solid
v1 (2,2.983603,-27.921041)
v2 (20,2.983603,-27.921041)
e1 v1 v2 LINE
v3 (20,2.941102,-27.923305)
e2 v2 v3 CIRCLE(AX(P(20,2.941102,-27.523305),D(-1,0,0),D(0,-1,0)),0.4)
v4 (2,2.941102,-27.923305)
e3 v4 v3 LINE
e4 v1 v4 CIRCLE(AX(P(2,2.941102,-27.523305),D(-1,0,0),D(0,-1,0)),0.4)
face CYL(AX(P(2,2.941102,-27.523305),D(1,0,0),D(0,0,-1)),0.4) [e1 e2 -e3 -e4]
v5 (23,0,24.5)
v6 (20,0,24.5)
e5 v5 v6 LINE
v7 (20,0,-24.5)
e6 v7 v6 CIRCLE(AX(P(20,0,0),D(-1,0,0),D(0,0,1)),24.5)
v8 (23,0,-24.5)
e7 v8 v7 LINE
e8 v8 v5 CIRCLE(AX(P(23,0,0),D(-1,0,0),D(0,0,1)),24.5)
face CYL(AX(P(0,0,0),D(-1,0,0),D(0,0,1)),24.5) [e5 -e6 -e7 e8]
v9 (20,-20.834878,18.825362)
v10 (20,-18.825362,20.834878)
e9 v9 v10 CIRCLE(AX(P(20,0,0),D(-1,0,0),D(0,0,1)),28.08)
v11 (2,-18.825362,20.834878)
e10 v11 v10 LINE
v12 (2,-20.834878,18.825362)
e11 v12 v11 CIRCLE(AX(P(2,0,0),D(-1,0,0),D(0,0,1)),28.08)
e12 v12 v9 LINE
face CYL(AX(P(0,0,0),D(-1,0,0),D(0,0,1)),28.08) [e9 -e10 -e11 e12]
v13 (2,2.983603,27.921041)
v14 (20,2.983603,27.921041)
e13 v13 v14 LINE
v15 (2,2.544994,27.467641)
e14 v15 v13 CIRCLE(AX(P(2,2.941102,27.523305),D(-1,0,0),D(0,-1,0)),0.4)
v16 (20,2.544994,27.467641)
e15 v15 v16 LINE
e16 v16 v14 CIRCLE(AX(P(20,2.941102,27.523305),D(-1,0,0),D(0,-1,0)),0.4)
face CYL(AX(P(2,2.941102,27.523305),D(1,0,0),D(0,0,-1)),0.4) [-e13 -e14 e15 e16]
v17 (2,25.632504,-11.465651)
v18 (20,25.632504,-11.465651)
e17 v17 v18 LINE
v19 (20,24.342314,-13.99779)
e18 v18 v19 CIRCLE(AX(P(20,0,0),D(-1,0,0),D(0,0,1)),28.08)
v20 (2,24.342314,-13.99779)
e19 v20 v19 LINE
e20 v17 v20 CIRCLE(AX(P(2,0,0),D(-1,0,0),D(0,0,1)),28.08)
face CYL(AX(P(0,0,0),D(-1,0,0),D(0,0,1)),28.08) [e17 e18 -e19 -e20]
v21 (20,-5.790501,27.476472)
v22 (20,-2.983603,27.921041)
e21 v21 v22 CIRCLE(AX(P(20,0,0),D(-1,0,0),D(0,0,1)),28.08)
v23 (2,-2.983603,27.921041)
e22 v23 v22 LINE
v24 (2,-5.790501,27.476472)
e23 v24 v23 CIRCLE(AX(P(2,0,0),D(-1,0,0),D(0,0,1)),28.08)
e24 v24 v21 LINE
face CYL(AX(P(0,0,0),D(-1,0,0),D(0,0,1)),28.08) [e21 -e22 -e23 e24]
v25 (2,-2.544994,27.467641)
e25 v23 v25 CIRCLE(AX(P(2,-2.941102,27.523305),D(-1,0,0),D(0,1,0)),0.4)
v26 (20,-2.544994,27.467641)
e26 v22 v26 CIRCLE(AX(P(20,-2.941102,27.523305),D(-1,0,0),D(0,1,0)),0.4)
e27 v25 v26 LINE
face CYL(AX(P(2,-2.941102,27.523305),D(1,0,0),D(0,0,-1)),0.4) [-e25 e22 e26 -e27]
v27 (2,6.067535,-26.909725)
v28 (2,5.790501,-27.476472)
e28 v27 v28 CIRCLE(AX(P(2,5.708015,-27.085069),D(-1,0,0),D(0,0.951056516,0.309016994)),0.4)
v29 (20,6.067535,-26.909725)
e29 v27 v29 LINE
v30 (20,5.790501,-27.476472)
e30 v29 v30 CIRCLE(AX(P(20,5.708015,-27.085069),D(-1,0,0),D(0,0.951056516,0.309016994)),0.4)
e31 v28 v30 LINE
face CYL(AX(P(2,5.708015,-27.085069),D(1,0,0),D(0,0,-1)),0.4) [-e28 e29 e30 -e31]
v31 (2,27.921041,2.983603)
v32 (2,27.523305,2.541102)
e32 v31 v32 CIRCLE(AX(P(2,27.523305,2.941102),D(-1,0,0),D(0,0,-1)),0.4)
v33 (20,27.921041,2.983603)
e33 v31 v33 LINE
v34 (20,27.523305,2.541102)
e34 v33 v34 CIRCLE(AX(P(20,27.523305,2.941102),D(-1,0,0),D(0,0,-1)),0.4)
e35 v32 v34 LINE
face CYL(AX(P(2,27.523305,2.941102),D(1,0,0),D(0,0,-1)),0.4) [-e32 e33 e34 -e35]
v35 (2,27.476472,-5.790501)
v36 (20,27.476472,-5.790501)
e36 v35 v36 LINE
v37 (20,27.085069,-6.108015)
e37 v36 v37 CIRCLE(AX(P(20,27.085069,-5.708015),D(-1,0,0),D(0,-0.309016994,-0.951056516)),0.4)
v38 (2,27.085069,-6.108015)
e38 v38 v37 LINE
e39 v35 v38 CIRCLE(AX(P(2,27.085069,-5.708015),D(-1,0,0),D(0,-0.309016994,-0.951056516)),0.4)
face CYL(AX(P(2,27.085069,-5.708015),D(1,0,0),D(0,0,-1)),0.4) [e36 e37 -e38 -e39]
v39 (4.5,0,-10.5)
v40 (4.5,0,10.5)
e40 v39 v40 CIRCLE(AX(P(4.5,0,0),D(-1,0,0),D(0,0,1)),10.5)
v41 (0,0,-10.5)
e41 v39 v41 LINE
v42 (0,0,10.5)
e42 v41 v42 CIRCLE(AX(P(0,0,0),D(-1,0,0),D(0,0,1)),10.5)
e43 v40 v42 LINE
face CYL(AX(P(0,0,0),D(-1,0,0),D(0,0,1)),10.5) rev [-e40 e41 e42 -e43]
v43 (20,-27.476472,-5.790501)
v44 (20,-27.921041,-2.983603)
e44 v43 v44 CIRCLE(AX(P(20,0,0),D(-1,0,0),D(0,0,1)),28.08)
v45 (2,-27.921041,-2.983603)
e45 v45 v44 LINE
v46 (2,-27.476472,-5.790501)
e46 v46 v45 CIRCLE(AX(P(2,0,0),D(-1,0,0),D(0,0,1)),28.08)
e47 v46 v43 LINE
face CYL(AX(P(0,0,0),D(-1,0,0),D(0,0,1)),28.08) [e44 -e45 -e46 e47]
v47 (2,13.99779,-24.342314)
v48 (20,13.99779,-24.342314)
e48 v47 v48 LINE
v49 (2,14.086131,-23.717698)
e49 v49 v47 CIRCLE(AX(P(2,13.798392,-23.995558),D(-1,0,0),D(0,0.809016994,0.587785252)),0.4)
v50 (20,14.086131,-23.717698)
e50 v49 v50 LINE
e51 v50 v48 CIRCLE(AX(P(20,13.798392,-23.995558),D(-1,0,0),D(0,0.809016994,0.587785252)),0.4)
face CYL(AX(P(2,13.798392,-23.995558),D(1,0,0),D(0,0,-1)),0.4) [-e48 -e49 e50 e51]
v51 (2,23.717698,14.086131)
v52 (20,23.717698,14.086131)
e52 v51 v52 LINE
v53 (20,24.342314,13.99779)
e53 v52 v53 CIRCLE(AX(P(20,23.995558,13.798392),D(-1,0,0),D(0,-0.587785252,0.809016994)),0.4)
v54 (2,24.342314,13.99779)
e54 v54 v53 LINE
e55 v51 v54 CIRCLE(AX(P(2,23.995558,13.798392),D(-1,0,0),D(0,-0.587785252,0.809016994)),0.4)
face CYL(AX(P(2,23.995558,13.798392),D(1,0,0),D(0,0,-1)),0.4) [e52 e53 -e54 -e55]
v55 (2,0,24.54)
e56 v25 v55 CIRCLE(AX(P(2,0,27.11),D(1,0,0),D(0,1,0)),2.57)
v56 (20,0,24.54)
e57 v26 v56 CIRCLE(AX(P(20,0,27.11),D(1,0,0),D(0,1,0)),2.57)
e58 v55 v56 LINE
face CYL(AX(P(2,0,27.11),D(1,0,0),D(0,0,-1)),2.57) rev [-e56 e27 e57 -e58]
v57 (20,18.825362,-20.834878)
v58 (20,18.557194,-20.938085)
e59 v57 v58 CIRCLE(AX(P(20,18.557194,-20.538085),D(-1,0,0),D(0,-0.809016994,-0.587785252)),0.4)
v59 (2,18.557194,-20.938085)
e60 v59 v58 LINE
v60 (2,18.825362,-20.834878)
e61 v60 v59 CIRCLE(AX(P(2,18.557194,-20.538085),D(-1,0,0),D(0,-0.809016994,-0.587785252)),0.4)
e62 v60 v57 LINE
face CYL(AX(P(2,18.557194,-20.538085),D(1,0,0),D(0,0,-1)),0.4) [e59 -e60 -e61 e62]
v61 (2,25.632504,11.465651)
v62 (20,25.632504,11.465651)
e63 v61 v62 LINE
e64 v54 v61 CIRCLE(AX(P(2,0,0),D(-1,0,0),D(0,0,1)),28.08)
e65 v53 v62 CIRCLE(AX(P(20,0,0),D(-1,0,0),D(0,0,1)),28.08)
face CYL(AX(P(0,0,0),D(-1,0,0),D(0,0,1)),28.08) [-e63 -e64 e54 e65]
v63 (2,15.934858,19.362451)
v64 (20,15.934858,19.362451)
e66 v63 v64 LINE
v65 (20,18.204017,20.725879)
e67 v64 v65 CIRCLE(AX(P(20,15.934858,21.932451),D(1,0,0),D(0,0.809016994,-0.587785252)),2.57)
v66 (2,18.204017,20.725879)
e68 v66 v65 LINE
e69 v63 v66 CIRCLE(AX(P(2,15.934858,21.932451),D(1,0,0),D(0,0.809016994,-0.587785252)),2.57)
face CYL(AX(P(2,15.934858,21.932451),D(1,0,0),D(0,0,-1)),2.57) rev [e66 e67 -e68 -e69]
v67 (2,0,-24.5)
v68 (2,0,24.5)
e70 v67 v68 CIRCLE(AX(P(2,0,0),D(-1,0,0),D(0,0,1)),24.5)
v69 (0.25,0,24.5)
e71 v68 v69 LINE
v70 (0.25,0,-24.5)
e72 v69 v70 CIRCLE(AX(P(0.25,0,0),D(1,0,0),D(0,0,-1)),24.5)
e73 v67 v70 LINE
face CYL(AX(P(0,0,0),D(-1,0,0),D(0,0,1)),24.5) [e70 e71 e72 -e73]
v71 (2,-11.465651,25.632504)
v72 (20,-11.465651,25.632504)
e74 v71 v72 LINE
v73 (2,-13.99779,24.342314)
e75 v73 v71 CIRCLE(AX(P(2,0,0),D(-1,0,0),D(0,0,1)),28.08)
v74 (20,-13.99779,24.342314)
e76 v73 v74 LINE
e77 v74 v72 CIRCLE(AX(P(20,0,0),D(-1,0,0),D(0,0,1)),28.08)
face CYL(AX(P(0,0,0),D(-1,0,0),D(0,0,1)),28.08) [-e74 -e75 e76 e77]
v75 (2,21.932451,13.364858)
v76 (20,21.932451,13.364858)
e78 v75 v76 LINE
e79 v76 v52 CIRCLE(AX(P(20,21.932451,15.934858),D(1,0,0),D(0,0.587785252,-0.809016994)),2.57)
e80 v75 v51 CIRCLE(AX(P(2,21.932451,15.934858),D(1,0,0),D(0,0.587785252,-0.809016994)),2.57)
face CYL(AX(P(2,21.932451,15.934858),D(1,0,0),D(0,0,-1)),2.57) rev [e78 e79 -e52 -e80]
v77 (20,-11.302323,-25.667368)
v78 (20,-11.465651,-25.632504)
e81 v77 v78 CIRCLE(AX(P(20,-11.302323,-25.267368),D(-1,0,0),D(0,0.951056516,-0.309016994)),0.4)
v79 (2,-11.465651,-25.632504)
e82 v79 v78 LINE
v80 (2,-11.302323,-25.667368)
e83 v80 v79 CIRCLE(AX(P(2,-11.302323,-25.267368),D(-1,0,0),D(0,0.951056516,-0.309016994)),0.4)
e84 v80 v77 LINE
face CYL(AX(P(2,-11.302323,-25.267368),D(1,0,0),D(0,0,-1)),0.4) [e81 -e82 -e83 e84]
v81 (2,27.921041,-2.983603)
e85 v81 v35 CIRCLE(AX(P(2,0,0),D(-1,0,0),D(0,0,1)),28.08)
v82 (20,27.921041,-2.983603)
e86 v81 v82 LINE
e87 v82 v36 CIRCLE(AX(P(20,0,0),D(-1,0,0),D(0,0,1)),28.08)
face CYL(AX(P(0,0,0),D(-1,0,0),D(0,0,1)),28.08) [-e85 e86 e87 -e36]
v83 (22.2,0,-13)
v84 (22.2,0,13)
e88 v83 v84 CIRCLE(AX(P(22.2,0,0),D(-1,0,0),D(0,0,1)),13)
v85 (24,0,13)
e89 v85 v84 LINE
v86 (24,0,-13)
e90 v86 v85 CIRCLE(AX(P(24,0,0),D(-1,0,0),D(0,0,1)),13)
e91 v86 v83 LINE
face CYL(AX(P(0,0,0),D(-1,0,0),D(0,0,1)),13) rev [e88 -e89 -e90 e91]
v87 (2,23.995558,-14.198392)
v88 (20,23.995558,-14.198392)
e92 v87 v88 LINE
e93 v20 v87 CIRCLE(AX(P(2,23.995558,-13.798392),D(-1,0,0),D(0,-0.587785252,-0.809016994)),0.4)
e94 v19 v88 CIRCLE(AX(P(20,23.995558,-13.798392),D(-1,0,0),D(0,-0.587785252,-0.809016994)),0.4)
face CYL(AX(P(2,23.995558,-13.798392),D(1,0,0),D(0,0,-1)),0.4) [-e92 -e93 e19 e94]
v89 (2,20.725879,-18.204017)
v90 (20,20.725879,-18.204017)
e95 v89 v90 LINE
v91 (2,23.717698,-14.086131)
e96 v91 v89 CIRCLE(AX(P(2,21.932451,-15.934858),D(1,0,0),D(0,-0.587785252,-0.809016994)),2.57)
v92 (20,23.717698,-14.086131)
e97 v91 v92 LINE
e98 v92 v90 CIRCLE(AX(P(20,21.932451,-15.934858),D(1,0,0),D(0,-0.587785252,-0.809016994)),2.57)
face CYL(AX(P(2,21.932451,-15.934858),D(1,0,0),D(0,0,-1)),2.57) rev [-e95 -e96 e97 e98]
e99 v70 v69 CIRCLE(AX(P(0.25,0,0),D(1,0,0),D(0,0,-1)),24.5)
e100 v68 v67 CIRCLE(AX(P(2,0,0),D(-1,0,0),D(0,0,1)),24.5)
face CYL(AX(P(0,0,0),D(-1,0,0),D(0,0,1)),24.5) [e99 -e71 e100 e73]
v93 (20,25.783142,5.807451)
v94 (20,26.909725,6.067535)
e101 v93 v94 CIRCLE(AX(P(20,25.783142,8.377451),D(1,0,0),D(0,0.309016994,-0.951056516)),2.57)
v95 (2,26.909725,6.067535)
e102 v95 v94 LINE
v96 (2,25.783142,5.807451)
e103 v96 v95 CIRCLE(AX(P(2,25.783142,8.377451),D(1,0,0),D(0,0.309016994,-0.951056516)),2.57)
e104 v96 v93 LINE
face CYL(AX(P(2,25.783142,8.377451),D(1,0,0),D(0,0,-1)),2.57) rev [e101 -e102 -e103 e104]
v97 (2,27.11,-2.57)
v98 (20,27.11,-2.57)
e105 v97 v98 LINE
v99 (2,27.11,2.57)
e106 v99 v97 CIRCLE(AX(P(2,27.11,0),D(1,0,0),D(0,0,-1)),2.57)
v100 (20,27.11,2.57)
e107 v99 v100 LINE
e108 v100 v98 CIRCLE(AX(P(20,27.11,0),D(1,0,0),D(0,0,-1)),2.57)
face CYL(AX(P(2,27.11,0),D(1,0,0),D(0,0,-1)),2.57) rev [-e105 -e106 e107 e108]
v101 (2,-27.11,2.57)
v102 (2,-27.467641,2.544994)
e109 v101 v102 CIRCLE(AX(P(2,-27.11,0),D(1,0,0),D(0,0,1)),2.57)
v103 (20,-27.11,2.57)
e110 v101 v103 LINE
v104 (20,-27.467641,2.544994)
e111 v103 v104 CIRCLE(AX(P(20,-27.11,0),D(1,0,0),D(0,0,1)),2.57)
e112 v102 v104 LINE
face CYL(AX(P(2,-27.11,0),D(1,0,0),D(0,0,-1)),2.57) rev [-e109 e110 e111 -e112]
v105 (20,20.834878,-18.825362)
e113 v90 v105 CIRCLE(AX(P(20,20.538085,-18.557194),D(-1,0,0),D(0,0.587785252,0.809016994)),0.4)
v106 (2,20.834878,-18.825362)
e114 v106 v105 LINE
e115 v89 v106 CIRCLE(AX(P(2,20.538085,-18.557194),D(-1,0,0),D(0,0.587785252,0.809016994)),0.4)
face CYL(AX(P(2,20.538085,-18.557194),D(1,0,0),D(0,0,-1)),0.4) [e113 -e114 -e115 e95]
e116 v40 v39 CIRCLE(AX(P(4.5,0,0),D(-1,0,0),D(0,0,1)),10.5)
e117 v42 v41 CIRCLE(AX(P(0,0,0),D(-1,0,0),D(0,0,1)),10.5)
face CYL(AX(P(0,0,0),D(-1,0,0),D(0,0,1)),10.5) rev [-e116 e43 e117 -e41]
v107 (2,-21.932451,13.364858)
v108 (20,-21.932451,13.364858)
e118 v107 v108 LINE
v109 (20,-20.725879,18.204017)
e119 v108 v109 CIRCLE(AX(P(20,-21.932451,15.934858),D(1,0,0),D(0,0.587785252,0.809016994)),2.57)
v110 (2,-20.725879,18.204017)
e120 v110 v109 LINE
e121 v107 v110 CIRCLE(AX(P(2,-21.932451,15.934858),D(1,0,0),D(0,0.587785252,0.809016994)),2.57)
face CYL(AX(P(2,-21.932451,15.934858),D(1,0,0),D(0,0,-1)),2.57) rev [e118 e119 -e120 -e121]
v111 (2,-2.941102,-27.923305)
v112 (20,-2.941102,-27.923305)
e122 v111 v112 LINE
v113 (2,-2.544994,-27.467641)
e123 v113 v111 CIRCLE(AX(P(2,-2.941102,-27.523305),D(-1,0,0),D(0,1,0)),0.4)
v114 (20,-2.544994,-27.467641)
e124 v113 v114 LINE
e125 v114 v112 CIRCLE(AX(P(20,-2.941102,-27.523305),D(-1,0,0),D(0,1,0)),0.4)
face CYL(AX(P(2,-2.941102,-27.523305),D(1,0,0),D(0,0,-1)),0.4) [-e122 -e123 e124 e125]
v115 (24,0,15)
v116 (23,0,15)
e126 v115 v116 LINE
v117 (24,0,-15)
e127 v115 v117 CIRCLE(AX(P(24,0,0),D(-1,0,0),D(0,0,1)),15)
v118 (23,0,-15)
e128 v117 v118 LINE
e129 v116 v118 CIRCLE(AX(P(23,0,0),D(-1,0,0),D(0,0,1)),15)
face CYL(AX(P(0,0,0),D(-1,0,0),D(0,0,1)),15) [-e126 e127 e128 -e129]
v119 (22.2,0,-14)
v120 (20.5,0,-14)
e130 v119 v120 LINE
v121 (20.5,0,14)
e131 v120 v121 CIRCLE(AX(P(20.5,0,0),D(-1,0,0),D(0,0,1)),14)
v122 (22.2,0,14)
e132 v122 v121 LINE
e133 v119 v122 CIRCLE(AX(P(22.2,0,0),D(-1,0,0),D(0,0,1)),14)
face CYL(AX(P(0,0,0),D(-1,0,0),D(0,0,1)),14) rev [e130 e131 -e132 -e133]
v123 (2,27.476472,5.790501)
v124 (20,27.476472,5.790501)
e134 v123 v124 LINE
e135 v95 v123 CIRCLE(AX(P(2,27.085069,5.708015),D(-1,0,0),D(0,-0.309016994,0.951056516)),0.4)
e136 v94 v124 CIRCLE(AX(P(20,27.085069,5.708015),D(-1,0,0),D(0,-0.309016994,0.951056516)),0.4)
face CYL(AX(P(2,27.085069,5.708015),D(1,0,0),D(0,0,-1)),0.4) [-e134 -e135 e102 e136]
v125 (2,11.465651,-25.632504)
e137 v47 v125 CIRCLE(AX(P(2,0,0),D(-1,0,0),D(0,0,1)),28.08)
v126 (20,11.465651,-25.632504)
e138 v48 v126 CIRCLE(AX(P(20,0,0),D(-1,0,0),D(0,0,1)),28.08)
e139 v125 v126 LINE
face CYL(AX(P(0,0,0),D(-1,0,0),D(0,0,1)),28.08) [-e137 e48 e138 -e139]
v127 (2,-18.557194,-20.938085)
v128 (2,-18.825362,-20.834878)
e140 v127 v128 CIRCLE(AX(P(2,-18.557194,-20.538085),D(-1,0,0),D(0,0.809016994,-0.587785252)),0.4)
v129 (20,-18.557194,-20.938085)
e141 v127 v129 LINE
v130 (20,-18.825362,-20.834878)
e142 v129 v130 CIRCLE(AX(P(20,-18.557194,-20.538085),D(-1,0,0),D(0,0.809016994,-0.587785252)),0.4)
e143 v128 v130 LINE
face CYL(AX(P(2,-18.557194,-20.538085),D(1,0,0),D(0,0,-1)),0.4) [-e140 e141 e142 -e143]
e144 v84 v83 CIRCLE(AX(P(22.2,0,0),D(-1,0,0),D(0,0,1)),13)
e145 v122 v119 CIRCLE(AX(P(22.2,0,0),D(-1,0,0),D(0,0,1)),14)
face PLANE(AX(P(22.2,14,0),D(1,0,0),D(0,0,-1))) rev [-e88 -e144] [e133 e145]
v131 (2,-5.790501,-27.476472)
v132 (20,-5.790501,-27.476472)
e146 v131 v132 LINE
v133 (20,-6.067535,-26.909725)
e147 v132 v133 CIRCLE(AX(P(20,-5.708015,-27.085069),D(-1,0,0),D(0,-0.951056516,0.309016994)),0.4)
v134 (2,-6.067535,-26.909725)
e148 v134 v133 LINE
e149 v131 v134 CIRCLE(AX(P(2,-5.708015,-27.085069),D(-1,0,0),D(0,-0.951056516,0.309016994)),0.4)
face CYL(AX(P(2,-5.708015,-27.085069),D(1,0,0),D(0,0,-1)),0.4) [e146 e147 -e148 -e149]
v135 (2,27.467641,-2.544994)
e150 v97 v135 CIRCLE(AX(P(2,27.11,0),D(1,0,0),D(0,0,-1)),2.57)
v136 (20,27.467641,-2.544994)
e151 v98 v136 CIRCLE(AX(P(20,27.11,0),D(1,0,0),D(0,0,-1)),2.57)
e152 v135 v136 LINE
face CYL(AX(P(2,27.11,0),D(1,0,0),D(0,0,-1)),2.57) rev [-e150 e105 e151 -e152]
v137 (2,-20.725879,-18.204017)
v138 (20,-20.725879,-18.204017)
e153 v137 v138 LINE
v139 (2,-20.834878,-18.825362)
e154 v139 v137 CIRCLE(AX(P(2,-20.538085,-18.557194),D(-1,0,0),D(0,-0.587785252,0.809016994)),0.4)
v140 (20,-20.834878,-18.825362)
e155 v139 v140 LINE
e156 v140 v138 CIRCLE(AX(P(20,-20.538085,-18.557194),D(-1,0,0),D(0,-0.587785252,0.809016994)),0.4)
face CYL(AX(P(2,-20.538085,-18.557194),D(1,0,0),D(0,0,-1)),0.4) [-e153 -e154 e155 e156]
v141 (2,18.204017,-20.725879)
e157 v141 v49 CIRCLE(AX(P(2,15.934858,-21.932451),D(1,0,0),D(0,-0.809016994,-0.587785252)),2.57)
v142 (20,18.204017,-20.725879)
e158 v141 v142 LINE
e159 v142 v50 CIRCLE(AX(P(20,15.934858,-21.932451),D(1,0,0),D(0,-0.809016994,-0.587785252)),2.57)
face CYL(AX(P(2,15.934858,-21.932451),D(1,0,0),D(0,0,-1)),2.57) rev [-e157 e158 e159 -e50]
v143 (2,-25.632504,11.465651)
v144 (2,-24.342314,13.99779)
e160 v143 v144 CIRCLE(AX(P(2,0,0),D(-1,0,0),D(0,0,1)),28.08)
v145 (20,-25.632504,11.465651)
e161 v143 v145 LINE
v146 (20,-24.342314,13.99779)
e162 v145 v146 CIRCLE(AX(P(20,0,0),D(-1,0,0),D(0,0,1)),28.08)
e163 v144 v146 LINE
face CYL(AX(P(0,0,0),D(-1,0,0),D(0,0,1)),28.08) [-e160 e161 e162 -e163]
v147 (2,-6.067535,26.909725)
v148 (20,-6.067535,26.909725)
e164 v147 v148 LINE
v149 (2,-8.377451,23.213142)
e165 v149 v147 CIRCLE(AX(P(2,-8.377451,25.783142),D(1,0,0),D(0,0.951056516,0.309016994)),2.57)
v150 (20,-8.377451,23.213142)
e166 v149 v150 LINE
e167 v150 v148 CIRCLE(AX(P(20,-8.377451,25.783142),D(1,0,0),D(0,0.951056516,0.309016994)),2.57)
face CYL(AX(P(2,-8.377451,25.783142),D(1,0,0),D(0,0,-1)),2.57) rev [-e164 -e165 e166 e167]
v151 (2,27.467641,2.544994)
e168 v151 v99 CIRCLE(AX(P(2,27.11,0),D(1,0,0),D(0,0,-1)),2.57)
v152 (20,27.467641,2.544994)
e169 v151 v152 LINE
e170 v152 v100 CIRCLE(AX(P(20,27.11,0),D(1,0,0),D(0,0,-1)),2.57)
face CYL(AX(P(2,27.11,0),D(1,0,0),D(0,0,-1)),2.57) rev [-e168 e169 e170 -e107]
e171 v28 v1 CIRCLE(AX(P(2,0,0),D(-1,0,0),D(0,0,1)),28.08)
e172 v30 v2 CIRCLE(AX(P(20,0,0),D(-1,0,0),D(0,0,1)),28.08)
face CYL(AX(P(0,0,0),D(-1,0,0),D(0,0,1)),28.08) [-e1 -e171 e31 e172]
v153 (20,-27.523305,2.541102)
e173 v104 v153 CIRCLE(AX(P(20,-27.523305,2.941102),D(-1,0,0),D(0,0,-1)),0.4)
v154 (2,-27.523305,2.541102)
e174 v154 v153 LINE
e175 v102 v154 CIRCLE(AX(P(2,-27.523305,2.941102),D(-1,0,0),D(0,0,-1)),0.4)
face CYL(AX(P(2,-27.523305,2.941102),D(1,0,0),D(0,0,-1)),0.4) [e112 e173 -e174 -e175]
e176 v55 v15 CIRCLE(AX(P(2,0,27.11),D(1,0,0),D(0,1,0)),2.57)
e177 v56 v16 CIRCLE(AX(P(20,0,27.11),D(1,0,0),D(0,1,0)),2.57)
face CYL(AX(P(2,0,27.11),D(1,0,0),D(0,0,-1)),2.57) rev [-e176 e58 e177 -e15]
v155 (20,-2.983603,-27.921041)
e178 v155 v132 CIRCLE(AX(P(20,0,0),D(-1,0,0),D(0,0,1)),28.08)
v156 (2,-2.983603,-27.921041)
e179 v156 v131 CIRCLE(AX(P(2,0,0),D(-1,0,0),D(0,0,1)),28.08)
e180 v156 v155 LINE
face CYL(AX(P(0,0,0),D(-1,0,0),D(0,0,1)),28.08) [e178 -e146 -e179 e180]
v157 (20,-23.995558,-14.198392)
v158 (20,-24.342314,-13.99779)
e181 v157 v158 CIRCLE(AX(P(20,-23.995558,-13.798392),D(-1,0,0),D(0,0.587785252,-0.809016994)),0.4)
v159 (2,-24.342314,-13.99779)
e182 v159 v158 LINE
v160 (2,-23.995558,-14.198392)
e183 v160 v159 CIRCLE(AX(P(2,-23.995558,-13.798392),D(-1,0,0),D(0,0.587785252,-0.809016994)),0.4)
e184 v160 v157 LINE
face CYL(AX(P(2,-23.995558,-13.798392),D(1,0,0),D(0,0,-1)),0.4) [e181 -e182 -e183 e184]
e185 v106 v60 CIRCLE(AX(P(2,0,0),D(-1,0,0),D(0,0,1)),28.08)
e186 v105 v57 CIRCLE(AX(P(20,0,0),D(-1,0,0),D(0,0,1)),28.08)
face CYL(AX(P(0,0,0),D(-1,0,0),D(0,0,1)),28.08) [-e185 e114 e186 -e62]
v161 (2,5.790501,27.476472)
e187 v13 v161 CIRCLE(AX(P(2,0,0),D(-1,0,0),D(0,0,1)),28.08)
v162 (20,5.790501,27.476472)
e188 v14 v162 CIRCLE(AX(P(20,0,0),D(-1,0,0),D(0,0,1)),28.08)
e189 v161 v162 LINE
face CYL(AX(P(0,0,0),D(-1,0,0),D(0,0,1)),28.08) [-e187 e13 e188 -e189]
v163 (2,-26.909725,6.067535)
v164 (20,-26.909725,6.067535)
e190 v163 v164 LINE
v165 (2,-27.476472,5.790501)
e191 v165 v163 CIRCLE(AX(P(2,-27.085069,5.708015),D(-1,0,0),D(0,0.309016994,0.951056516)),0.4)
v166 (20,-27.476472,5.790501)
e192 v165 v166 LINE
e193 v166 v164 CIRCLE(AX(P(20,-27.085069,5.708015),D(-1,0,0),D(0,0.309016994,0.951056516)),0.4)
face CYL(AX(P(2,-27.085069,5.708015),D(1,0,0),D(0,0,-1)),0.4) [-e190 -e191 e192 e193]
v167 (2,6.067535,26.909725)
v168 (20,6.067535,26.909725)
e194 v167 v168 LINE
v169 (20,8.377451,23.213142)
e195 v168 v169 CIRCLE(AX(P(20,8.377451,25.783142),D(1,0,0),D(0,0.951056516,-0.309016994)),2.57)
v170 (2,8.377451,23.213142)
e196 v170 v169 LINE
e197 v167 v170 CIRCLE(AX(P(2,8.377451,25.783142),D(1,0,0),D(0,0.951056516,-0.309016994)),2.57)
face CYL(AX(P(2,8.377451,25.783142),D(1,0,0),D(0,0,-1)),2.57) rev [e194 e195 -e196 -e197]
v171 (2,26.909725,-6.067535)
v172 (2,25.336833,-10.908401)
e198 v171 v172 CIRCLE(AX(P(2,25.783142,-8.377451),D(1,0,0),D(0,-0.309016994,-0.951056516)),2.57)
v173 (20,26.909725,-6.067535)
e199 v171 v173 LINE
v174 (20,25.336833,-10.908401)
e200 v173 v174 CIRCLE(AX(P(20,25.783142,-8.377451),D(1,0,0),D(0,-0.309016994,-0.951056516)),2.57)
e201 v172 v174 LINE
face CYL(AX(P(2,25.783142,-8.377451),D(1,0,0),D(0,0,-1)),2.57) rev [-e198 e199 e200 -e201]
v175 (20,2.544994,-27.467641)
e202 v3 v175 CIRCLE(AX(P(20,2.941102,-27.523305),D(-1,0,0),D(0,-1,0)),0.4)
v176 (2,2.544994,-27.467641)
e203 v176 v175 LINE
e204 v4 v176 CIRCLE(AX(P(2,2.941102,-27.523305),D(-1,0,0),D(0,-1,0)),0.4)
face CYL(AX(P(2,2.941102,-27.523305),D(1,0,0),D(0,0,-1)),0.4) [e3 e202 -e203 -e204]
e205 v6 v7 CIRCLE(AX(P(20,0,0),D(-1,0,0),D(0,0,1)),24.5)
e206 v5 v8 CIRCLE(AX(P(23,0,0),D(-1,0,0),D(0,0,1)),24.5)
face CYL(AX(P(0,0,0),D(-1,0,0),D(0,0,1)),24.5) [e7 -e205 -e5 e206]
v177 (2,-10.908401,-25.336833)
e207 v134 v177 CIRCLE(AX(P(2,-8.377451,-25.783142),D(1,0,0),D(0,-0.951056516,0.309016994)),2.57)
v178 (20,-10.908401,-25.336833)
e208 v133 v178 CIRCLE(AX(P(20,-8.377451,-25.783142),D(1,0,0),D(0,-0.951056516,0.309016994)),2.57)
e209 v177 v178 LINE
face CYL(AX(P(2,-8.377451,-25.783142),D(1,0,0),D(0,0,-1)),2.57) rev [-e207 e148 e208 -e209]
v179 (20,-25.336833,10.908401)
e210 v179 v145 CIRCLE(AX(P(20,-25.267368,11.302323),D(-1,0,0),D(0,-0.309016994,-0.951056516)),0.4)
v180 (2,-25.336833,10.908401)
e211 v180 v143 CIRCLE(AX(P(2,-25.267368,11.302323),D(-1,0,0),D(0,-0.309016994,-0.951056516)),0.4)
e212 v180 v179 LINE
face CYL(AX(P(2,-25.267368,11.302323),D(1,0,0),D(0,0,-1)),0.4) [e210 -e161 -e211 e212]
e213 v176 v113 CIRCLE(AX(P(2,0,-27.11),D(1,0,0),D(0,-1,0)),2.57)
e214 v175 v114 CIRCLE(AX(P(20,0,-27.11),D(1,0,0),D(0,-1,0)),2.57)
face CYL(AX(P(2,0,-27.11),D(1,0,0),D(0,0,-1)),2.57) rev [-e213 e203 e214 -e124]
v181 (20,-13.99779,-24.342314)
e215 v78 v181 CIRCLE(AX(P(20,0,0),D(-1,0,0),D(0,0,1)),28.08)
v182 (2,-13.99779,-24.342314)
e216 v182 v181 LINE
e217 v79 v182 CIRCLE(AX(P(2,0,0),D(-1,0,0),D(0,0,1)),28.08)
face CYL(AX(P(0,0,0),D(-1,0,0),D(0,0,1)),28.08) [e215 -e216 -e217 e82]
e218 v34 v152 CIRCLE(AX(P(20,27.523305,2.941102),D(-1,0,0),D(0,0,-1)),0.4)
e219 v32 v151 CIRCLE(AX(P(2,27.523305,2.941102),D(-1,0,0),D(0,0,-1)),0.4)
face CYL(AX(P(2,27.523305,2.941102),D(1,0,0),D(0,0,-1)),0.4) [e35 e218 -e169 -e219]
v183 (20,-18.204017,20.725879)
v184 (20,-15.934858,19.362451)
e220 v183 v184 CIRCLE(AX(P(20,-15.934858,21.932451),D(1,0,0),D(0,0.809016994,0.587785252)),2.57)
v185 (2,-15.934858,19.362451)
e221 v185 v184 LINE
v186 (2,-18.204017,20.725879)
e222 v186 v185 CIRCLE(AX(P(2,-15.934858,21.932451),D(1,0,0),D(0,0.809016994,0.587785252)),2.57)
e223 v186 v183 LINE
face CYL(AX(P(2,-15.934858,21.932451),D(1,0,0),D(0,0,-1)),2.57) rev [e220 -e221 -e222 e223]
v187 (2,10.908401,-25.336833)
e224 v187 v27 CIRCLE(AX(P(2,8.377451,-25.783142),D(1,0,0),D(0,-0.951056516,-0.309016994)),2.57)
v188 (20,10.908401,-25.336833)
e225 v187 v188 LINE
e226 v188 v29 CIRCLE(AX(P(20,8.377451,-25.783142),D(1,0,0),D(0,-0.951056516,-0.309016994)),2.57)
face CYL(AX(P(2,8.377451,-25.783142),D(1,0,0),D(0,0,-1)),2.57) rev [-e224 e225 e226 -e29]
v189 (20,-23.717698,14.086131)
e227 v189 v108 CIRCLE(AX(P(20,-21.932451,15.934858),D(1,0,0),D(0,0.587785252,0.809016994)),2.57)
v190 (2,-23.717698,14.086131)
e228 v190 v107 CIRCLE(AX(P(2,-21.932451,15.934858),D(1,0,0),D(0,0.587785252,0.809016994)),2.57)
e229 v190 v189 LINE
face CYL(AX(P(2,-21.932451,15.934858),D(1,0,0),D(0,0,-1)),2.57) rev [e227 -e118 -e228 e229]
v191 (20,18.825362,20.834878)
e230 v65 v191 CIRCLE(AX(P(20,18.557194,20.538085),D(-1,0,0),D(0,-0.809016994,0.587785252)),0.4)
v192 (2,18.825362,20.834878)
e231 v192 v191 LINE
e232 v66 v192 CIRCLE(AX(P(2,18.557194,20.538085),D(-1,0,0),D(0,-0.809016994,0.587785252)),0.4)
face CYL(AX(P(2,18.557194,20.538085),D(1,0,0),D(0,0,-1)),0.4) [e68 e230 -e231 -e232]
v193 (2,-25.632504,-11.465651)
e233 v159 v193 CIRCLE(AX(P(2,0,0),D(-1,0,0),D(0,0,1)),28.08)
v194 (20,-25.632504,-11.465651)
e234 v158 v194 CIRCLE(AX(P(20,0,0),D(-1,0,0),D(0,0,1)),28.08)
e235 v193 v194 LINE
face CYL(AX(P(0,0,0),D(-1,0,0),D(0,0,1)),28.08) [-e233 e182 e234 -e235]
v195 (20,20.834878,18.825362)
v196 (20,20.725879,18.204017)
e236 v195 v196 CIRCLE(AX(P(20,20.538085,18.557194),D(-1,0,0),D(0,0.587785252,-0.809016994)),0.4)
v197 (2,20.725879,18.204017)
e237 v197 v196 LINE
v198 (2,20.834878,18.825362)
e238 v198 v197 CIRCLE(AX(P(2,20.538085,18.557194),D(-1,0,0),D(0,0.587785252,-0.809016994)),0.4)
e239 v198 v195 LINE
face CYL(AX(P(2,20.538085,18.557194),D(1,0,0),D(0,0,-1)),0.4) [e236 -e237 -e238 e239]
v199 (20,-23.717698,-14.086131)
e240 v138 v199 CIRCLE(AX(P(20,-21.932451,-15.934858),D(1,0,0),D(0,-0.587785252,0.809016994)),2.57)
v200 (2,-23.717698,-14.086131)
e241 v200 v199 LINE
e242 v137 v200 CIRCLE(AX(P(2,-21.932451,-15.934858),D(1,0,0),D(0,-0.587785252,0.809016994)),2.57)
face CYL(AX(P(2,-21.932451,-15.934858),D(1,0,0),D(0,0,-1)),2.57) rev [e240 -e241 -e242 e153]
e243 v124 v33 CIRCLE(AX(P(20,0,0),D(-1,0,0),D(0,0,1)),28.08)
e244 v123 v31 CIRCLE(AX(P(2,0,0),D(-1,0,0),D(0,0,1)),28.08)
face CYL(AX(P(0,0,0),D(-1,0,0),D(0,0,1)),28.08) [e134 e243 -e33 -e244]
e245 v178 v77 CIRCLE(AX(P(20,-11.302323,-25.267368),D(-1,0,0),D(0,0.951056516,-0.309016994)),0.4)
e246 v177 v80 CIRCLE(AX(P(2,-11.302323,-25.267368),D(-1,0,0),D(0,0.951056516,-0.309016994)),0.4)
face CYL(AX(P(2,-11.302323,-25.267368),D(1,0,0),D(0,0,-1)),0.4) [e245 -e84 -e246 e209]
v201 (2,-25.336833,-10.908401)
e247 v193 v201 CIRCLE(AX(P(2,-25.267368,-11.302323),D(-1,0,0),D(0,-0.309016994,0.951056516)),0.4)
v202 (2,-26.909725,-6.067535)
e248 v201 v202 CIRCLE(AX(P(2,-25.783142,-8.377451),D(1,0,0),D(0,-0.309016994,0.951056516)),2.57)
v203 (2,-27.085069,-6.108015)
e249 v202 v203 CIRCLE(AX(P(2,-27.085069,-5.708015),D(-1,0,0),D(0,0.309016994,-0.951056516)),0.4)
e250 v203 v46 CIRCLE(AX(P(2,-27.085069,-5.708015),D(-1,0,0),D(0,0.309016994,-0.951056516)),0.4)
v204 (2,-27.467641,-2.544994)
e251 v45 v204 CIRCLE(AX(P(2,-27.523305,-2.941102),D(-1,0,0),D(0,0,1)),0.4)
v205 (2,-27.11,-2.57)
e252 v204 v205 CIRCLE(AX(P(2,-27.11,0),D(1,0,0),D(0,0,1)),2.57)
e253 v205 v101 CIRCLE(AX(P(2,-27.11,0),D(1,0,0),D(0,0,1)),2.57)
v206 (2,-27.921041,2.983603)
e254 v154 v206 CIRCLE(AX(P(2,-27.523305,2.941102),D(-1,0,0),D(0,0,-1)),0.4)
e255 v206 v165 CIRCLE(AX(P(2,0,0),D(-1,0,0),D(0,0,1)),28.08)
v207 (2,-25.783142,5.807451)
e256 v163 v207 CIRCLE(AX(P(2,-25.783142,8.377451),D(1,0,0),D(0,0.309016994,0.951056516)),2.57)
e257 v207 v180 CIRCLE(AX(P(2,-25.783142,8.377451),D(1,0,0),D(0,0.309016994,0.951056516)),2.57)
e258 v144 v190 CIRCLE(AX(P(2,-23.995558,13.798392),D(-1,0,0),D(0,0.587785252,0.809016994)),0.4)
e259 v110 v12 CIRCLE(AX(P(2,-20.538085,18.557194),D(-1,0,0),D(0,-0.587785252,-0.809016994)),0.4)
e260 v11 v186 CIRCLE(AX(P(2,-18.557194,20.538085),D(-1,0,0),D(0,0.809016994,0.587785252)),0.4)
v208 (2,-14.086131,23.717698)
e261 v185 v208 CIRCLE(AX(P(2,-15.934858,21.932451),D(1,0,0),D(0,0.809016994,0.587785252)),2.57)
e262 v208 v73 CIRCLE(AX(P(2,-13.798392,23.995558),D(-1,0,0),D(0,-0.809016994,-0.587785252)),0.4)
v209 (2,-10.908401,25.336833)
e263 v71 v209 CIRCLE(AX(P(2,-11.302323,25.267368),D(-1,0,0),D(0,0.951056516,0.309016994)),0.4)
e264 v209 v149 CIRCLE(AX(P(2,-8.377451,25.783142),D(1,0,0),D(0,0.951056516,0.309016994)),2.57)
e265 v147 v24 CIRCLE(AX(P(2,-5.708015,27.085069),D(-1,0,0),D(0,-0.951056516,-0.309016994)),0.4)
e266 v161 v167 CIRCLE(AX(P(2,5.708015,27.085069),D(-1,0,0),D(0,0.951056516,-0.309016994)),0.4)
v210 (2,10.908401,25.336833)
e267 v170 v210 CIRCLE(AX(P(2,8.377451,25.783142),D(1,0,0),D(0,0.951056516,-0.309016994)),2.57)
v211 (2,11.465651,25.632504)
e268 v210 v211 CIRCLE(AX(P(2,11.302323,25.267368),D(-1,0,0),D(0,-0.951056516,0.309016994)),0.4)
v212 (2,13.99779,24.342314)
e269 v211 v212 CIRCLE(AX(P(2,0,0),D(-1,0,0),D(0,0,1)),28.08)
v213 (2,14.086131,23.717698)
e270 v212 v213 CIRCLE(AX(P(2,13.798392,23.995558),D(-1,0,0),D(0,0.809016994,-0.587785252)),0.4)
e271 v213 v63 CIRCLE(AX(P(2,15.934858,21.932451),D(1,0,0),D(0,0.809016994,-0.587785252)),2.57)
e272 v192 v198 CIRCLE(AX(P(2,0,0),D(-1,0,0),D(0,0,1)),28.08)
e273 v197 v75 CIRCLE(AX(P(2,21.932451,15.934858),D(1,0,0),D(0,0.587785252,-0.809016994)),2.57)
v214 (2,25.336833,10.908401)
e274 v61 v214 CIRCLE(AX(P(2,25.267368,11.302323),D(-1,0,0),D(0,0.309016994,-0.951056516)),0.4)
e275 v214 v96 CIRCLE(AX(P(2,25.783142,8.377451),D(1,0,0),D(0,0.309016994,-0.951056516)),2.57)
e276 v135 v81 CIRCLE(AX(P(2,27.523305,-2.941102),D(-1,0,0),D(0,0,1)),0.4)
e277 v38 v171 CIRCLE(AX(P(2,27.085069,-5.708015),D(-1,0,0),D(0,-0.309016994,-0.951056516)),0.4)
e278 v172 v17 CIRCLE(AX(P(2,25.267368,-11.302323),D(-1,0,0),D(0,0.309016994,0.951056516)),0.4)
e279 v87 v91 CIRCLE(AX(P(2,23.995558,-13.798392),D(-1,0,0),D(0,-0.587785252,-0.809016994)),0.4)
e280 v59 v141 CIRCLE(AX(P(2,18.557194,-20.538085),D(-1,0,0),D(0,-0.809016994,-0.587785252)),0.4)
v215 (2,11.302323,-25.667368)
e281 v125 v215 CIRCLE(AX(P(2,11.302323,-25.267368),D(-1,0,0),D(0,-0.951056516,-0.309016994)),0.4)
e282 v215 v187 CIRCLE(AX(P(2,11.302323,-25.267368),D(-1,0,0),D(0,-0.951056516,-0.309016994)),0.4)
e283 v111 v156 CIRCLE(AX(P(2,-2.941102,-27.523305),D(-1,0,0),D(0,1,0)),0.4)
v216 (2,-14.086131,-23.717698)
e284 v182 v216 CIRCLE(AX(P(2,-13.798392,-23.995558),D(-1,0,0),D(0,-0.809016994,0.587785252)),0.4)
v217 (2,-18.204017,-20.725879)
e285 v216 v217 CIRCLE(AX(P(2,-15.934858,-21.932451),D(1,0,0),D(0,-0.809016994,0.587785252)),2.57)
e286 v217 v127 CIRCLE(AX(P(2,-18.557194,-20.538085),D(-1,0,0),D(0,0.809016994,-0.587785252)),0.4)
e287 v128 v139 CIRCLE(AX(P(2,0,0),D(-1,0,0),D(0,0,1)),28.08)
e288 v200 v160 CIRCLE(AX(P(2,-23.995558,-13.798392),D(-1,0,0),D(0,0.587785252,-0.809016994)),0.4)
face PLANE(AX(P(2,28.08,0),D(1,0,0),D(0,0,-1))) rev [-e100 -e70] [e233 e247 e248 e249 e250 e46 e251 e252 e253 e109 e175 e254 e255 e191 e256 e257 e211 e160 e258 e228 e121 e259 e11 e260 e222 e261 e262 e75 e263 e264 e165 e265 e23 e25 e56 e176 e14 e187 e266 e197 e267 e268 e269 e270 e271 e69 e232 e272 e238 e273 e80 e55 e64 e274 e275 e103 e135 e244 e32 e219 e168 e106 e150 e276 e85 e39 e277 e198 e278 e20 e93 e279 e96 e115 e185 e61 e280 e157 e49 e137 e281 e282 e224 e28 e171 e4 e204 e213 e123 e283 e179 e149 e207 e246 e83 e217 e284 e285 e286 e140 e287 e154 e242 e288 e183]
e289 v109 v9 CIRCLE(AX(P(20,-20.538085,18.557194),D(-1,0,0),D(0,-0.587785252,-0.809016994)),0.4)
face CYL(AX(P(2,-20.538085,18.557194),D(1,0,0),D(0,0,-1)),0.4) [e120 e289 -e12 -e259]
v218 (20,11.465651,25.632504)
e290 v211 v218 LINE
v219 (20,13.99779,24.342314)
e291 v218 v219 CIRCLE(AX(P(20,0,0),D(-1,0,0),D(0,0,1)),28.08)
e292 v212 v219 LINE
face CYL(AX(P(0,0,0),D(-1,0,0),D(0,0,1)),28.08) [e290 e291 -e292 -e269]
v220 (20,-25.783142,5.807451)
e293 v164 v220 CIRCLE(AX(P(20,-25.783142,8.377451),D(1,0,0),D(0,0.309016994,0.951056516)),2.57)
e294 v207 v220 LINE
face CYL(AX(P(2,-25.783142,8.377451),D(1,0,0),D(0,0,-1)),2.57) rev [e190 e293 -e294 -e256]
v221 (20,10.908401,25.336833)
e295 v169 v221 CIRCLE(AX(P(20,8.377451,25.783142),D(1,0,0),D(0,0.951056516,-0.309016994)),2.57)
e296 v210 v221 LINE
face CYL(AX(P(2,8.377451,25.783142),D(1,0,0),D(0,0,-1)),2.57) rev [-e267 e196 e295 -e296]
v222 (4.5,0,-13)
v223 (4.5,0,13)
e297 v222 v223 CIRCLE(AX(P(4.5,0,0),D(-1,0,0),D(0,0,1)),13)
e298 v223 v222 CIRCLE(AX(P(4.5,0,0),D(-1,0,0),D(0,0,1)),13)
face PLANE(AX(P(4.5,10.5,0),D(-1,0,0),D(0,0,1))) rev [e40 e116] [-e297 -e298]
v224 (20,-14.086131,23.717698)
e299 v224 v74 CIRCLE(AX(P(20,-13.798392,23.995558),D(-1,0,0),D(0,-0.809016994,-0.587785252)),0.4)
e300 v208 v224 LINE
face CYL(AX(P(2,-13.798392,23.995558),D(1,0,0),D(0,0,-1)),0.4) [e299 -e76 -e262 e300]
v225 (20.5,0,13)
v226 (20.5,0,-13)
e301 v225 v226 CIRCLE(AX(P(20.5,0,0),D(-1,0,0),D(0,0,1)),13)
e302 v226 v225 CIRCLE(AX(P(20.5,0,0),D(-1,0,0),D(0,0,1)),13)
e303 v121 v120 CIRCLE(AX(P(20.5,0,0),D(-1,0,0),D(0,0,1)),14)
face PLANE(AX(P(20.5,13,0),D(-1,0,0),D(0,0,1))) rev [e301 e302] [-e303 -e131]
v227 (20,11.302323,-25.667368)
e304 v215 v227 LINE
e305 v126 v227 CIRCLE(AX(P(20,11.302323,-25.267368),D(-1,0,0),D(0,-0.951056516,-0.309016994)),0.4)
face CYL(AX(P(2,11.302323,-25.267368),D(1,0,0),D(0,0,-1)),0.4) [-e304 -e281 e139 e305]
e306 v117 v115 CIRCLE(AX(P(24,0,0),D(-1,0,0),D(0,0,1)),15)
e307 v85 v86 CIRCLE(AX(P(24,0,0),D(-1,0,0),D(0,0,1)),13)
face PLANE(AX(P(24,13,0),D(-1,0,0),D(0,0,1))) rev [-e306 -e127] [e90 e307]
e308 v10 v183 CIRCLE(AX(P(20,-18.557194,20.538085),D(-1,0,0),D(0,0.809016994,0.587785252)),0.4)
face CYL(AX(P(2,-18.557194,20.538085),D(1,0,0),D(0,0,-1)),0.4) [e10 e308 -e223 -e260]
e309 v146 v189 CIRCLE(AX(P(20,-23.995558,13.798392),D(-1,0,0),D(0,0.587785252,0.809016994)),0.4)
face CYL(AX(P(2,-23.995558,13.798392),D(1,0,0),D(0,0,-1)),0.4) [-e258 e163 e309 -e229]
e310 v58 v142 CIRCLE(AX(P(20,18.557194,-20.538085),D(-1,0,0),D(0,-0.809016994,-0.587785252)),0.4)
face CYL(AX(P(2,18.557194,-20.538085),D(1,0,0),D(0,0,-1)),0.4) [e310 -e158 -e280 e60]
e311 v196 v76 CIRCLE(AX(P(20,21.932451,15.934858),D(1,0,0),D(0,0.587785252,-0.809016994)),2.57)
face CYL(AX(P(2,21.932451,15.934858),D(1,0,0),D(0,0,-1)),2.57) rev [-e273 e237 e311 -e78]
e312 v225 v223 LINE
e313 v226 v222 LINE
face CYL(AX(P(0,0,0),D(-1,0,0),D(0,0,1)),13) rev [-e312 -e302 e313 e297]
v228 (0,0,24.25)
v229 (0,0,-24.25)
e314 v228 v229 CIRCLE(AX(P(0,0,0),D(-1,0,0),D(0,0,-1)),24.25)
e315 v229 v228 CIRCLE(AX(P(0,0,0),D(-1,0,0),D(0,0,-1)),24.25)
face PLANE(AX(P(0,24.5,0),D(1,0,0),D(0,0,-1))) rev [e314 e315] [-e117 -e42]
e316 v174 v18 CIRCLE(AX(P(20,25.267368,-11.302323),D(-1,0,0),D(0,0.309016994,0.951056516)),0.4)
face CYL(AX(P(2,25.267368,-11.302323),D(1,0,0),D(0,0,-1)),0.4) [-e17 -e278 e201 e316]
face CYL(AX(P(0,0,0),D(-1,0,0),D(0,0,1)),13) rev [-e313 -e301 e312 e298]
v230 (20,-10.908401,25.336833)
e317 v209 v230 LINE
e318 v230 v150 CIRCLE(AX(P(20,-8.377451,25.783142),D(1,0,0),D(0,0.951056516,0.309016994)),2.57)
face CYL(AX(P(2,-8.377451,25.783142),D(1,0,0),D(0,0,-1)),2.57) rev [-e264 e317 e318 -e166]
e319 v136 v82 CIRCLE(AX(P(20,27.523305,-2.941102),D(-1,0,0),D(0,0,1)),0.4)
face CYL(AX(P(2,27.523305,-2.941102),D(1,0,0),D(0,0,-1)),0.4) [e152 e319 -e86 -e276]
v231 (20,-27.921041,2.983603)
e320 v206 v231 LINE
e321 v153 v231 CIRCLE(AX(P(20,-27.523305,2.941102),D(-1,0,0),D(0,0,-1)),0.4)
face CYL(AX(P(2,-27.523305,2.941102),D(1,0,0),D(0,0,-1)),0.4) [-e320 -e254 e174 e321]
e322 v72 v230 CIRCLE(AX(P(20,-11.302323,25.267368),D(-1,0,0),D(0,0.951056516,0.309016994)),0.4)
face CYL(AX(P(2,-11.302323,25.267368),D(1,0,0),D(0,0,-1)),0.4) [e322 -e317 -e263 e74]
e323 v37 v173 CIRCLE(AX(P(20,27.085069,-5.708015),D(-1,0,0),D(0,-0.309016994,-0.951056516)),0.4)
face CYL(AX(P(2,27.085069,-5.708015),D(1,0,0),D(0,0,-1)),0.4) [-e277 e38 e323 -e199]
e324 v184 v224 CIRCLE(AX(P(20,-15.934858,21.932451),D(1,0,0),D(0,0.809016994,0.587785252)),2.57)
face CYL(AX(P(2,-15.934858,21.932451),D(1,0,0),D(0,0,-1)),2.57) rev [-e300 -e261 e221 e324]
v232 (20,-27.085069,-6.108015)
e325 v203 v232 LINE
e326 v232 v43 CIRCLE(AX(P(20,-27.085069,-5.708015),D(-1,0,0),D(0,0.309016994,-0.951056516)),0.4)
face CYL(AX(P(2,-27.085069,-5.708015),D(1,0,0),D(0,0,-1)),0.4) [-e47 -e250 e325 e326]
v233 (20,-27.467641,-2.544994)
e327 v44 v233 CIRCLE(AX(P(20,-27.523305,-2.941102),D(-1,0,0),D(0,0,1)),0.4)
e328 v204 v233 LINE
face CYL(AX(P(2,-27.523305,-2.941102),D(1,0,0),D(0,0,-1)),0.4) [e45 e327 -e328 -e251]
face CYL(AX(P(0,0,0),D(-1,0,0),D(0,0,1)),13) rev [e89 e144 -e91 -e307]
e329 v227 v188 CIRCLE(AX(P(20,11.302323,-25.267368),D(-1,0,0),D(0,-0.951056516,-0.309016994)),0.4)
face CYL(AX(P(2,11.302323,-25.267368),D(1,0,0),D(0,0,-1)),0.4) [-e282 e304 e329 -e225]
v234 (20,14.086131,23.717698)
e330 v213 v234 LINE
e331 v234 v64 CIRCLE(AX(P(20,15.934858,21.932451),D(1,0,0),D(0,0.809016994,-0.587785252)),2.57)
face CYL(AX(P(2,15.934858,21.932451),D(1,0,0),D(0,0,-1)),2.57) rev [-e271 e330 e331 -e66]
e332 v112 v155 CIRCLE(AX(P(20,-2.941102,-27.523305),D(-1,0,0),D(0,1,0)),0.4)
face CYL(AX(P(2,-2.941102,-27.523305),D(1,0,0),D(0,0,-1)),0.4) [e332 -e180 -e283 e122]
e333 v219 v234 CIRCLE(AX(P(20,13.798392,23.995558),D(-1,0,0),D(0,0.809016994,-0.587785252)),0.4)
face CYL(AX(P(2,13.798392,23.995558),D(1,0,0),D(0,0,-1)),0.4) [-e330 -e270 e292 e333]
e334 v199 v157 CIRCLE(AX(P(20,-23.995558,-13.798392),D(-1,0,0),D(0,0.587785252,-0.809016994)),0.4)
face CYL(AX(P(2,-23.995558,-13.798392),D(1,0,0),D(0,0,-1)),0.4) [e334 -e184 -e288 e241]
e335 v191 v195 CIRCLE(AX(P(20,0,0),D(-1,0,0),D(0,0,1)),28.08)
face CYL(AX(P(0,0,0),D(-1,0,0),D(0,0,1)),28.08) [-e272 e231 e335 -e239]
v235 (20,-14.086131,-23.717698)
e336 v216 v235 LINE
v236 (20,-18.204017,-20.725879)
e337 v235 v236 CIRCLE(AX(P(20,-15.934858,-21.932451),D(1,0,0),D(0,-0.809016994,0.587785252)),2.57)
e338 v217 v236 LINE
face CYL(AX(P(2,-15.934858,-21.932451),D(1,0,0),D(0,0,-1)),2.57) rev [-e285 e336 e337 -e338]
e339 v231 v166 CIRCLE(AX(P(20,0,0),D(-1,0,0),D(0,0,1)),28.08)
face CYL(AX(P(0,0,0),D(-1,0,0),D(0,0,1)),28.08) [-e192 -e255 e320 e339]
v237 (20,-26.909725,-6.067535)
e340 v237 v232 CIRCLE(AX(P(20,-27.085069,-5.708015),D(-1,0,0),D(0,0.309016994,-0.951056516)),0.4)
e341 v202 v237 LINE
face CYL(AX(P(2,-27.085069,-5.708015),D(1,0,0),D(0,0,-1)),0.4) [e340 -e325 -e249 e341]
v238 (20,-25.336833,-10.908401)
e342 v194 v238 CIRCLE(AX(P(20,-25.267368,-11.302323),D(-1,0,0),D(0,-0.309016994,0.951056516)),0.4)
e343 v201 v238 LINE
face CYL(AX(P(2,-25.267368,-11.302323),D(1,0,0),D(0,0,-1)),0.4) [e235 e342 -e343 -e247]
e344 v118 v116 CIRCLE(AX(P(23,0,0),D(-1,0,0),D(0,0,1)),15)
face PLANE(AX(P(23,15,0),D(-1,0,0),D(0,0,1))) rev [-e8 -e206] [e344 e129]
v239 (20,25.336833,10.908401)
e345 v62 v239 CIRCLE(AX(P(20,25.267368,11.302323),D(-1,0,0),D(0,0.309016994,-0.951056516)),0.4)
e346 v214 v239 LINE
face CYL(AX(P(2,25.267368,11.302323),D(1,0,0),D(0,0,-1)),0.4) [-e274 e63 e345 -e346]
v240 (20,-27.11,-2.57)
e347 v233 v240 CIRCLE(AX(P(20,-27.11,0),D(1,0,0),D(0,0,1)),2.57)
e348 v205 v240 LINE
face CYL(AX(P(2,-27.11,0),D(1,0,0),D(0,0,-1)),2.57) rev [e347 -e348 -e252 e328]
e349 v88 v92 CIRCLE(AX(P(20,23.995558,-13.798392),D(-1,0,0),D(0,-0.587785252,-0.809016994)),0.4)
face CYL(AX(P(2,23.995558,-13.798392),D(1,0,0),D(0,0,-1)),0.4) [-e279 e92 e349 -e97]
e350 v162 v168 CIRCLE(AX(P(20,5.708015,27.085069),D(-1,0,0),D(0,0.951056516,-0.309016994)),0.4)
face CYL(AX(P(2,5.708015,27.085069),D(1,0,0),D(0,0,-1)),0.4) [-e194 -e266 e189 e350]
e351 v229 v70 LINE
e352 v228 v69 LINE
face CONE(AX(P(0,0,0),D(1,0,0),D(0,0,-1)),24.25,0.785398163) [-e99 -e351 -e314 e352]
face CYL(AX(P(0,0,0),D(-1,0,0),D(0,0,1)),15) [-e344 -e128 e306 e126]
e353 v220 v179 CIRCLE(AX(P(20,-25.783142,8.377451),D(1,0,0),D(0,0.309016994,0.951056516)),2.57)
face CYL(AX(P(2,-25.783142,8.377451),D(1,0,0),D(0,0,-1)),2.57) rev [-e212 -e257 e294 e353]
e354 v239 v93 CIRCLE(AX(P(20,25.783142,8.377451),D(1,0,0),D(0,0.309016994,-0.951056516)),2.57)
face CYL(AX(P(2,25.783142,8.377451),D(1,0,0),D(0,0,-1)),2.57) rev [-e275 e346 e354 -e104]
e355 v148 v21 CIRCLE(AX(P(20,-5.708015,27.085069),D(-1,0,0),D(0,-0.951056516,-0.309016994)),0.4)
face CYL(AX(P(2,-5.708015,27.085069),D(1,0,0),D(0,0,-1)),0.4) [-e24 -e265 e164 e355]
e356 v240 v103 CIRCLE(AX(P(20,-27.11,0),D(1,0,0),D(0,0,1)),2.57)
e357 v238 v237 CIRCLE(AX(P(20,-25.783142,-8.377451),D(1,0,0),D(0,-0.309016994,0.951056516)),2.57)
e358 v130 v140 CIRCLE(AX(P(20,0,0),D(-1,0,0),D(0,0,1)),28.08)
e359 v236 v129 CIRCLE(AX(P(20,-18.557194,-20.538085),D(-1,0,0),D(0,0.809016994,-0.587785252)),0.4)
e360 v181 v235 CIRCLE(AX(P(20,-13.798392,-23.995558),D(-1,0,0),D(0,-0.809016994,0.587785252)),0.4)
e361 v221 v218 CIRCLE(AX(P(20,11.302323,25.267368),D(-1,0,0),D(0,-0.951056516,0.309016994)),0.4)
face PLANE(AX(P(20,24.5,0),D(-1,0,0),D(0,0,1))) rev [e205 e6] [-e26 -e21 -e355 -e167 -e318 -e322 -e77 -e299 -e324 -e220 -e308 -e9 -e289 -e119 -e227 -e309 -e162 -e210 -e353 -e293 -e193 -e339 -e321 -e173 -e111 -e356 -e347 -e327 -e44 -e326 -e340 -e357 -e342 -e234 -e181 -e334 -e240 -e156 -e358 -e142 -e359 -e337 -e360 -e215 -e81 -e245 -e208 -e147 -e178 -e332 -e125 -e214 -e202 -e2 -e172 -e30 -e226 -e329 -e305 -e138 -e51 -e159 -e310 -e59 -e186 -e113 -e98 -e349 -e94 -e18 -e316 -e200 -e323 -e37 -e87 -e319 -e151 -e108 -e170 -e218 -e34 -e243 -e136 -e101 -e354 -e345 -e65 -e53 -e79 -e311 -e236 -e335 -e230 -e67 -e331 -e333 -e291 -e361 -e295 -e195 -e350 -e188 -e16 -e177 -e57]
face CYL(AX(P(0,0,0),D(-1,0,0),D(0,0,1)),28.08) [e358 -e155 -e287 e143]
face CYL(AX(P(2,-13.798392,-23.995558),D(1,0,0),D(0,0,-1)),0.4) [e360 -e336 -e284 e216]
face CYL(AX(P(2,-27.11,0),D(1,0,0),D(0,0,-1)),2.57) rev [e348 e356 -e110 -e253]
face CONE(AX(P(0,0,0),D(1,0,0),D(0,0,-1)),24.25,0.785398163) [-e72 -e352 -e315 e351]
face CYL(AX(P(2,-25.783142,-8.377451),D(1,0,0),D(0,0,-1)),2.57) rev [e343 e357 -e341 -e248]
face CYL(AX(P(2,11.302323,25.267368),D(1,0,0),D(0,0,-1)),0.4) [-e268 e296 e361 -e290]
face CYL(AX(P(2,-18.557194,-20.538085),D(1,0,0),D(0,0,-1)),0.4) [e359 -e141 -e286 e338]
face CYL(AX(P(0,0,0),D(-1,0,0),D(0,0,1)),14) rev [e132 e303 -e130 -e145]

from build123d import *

# Parameters (mm, degrees)
CHAMFER_1_SIZE           = 0.25
CUT_EXTRUDE_START        = -18
CUT_EXTRUDE_1_DEPTH      = 18
PATTERN_CIRCULAR_1_COUNT = 20


with BuildPart() as part:
    # 草图1 → 旋转2 (revolve)
    with BuildSketch(Plane.XY, mode=Mode.PRIVATE) as revolve_2_sk:
        Polygon((0, 10.5), (4.5, 10.5), (4.5, 13), (20.5, 13), (20.5, 14), (22.2, 14), (22.2, 13), (24, 13), (24, 15), (23, 15), (23, 24.5), (20, 24.5), (20, 28.08), (2, 28.08), (2, 24.5), (0, 24.5), align=None)
    revolve(revolve_2_sk.sketch.rotate(Axis((0, 0, 0), (1, 0, 0)), 90), axis=Axis((0, 0, 0), (1, 0, 0)))

    # 倒角1
    chamfer_1_edges = [part.edges().sort_by_distance(p)[0] for p in [
        (0, 0, -24.5),
    ]]
    chamfer(chamfer_1_edges, length=CHAMFER_1_SIZE)

    # 草图2 → 切除-拉伸1 (cut)
    with BuildSketch(Plane(origin=(20, 0, 0), x_dir=(0, 0, -1), z_dir=(1, 0, 0)).offset(CUT_EXTRUDE_START)):
        with BuildLine():
            ThreePointArc((2.983603122, 27.921040676), (0, 28.08), (-2.983603122, 27.921040676))
            ThreePointArc((-2.983603122, 27.921040676), (-2.653608716, 27.801419798), (-2.544993686, 27.467641073))
            ThreePointArc((-2.544993686, 27.467641073), (0, 24.54), (2.544993686, 27.467641073))
            ThreePointArc((2.544993686, 27.467641073), (2.653608716, 27.801419798), (2.983603122, 27.921040676))
        make_face()
    cut_extrude_1 = extrude(amount=CUT_EXTRUDE_1_DEPTH, mode=Mode.SUBTRACT)

    # 阵列(圆周)1: 切除-拉伸1 ×20 about axis
    pattern_circular_1_axis = Axis((0, 0, 0), (1, 0, 0))
    for i in range(1, PATTERN_CIRCULAR_1_COUNT):
        add(cut_extrude_1.rotate(pattern_circular_1_axis, i * 360 / PATTERN_CIRCULAR_1_COUNT), mode=Mode.SUBTRACT)


solid = part.part
